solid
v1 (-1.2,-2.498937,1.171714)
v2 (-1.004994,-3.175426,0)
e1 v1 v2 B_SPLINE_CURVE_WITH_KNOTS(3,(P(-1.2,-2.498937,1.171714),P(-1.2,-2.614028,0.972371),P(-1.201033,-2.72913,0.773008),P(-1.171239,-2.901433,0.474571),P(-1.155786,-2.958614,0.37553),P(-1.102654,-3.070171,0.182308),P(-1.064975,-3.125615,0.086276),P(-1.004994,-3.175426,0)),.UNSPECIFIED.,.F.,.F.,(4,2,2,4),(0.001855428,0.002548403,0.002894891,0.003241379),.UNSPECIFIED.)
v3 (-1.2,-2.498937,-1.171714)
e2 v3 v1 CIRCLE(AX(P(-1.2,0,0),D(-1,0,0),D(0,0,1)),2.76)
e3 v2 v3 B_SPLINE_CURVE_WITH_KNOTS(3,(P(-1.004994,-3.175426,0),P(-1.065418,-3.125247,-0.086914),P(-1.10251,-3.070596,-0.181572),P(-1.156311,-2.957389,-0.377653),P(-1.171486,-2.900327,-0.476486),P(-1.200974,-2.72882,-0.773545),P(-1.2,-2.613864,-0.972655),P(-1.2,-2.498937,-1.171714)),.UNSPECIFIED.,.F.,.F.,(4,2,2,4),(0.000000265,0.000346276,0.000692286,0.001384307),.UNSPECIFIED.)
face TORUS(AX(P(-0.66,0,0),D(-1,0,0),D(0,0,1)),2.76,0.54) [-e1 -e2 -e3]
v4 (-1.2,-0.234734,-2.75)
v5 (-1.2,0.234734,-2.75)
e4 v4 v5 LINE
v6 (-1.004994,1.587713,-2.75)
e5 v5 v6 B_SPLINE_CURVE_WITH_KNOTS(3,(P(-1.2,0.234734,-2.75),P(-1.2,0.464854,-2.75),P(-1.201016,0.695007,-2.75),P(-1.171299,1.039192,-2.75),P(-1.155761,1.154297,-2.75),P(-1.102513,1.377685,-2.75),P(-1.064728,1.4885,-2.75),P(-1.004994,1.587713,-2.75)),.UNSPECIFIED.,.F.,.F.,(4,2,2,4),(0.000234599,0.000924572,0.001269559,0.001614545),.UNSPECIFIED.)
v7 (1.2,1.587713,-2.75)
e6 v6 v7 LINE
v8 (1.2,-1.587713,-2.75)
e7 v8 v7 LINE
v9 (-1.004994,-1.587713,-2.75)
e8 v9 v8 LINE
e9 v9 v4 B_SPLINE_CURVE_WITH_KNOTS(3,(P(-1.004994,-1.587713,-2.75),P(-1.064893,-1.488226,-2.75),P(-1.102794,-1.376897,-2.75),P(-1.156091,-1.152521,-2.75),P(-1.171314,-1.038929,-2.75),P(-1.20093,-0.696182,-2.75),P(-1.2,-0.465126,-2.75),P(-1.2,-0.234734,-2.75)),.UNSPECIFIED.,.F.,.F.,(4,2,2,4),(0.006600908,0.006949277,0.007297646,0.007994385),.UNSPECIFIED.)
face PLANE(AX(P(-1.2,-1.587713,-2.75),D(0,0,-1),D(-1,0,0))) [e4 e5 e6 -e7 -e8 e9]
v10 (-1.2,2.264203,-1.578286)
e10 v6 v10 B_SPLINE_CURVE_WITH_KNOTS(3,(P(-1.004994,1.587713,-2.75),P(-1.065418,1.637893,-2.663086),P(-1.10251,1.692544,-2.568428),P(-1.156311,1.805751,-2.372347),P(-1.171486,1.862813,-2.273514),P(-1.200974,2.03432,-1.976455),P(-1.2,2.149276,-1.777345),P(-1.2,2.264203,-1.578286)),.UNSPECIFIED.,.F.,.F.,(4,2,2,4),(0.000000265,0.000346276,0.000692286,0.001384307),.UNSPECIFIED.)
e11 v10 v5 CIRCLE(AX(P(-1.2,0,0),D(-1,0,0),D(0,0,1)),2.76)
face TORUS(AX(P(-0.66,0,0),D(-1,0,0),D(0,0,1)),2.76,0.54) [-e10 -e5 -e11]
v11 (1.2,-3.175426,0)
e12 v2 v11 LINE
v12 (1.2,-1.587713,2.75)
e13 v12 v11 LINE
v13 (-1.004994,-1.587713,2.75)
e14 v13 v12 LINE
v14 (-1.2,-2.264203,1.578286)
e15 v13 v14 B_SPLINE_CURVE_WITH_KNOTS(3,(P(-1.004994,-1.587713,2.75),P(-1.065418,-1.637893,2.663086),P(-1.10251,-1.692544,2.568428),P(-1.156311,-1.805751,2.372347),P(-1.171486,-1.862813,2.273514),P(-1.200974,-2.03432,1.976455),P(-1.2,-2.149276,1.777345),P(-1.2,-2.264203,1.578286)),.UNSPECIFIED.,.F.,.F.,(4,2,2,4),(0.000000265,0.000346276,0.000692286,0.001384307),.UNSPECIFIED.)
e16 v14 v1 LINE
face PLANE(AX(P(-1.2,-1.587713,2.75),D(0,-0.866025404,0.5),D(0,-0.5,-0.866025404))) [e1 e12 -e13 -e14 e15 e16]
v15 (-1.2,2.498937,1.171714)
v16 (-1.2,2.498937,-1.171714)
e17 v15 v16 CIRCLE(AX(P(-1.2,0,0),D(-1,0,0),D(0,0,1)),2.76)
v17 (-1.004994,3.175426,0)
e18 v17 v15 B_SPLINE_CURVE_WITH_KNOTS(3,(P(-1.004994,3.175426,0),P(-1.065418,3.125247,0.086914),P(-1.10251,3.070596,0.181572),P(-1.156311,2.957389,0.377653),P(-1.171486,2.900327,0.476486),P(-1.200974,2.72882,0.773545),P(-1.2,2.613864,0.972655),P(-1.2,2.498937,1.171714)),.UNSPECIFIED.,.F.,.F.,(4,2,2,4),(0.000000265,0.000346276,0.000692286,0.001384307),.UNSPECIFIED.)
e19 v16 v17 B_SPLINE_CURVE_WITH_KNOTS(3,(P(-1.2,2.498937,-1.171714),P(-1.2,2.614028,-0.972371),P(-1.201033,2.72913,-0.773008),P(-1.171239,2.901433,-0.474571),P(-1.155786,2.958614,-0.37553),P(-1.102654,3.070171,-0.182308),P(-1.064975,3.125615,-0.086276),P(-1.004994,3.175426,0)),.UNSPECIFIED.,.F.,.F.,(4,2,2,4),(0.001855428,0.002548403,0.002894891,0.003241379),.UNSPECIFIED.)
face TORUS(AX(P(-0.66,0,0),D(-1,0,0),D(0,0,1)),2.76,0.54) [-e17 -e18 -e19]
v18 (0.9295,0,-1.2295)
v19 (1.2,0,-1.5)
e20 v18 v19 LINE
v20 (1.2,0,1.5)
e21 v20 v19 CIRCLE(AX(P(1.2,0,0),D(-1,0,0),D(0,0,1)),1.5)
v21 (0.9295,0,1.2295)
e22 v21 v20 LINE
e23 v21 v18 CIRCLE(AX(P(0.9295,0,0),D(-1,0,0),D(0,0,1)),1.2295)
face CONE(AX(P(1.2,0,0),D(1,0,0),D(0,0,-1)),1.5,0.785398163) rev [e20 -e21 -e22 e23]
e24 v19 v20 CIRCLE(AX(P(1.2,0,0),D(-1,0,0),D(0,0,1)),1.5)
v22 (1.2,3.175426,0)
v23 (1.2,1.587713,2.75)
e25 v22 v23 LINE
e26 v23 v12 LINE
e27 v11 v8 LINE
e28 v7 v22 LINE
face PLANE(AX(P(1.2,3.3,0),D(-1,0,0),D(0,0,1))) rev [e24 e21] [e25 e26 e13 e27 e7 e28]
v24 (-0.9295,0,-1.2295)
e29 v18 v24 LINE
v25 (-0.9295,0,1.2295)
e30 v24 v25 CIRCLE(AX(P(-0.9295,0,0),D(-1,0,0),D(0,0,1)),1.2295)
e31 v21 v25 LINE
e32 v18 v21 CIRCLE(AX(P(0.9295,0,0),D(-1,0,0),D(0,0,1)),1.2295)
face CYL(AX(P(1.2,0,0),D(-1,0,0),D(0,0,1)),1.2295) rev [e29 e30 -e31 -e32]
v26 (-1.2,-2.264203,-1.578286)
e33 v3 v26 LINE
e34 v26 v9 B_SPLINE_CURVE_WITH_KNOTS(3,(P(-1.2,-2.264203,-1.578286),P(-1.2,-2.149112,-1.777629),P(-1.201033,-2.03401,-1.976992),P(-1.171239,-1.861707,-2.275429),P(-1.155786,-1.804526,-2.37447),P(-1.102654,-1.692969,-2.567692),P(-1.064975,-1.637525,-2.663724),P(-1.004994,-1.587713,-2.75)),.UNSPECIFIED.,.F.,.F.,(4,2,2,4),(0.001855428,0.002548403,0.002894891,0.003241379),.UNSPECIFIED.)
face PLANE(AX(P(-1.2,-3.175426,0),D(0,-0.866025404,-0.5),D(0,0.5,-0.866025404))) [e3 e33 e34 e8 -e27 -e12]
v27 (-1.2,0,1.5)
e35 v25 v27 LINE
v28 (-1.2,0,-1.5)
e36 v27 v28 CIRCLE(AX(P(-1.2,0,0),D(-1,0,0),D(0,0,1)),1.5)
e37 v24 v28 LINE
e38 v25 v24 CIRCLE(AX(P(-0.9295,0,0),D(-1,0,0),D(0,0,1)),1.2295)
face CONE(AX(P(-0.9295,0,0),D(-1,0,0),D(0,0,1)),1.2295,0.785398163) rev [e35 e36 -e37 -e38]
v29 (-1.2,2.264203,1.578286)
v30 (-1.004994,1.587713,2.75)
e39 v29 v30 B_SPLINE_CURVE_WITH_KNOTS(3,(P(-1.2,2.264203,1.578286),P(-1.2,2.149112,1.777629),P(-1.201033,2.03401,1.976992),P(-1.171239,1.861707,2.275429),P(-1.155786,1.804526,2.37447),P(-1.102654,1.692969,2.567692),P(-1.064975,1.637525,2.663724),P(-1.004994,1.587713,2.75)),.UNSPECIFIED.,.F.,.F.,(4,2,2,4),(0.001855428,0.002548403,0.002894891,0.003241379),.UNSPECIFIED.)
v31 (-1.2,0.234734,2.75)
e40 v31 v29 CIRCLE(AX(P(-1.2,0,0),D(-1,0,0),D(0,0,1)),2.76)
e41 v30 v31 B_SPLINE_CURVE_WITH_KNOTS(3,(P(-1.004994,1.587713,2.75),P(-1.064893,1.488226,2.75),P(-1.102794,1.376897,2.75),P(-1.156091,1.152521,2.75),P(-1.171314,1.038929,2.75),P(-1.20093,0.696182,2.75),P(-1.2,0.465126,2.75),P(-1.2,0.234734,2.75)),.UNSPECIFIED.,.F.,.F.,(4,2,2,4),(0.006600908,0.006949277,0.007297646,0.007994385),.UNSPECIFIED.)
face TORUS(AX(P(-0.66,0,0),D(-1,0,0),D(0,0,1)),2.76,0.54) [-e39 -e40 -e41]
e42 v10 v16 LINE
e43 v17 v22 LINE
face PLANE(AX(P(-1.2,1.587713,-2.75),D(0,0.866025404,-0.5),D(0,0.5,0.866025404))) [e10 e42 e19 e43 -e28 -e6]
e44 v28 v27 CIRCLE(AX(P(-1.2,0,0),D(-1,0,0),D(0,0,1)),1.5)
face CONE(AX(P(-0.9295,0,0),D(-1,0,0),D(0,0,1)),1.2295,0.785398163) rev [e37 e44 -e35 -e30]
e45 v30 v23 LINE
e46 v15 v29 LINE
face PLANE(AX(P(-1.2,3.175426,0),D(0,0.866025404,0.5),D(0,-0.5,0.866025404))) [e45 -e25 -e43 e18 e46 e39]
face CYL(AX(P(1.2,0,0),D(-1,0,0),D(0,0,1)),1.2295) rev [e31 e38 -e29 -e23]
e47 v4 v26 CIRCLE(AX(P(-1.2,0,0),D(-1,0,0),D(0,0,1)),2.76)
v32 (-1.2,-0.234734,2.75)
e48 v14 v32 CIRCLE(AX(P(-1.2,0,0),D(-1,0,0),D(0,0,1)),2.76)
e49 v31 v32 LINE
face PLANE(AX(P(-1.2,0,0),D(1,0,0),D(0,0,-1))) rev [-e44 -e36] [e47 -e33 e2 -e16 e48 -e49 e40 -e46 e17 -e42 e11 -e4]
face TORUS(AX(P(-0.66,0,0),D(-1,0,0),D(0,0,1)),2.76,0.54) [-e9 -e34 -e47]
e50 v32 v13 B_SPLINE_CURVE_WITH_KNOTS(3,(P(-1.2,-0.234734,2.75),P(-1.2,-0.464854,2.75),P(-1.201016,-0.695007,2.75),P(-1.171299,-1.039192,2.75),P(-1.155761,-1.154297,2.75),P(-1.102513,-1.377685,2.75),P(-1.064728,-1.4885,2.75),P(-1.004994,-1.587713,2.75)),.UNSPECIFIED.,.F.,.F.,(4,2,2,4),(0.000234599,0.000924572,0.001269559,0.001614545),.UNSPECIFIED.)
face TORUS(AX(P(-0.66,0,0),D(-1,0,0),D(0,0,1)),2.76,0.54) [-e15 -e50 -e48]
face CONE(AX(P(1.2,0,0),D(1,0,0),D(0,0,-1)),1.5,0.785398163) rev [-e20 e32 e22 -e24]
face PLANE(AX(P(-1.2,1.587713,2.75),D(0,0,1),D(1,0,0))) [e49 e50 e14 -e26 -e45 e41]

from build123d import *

# Parameters (mm, degrees)
CUT_EXTRUDE1_DEPTH      = 1.2
CUT_EXTRUDE1_DEPTH_BACK = 1.2
SKETCH3_W               = 11
SKETCH3_H               = 11


with BuildPart() as part:
    # Sketch1 → Revolve1 (revolve)
    with BuildSketch(Plane.XY, mode=Mode.PRIVATE) as revolve1_sk:
        with BuildLine():
            Line((-1.2, 0), (-1.2, 2.76))
            ThreePointArc((-1.2, 2.76), (-1.041837662, 3.141837662), (-0.66, 3.3))
            Line((-0.66, 3.3), (1.2, 3.3))
            Line((1.2, 3.3), (1.2, 0))
            Line((1.2, 0), (-1.2, 0))
        make_face()
    revolve(revolve1_sk.sketch.rotate(Axis((1.2, 0, 0), (-1, 0, 0)), 270), axis=Axis((1.2, 0, 0), (-1, 0, 0)))

    # Sketch2 → Cut-Revolve1 (revolve, cut)
    with BuildSketch(Plane.XY, mode=Mode.PRIVATE) as cut_revolve1_sk:
        Polygon((-1.2, 0), (-1.2, 1.5), (-0.9295, 1.2295), (0.9295, 1.2295), (1.2, 1.5), (1.2, 0), align=None)
    revolve(cut_revolve1_sk.sketch.rotate(Axis((1.2, 0, 0), (-1, 0, 0)), 270), axis=Axis((1.2, 0, 0), (-1, 0, 0)), mode=Mode.SUBTRACT)

    # Sketch3 → Cut-Extrude1 (cut, two sides: drawn at the far end of the back side and taken through both)
    with BuildSketch(Plane(origin=(0, 0, 0), x_dir=(0, 0, -1), z_dir=(1, 0, 0)).offset(-CUT_EXTRUDE1_DEPTH_BACK)):
        Rectangle(SKETCH3_W, SKETCH3_H)
        Polygon((-2.75, 1.58771324), (-2.75, -1.58771324), (0, -3.175426481), (2.75, -1.58771324), (2.75, 1.58771324), (0, 3.175426481), align=None, mode=Mode.SUBTRACT)
    extrude(amount=CUT_EXTRUDE1_DEPTH + CUT_EXTRUDE1_DEPTH_BACK, mode=Mode.SUBTRACT)


solid = part.part
